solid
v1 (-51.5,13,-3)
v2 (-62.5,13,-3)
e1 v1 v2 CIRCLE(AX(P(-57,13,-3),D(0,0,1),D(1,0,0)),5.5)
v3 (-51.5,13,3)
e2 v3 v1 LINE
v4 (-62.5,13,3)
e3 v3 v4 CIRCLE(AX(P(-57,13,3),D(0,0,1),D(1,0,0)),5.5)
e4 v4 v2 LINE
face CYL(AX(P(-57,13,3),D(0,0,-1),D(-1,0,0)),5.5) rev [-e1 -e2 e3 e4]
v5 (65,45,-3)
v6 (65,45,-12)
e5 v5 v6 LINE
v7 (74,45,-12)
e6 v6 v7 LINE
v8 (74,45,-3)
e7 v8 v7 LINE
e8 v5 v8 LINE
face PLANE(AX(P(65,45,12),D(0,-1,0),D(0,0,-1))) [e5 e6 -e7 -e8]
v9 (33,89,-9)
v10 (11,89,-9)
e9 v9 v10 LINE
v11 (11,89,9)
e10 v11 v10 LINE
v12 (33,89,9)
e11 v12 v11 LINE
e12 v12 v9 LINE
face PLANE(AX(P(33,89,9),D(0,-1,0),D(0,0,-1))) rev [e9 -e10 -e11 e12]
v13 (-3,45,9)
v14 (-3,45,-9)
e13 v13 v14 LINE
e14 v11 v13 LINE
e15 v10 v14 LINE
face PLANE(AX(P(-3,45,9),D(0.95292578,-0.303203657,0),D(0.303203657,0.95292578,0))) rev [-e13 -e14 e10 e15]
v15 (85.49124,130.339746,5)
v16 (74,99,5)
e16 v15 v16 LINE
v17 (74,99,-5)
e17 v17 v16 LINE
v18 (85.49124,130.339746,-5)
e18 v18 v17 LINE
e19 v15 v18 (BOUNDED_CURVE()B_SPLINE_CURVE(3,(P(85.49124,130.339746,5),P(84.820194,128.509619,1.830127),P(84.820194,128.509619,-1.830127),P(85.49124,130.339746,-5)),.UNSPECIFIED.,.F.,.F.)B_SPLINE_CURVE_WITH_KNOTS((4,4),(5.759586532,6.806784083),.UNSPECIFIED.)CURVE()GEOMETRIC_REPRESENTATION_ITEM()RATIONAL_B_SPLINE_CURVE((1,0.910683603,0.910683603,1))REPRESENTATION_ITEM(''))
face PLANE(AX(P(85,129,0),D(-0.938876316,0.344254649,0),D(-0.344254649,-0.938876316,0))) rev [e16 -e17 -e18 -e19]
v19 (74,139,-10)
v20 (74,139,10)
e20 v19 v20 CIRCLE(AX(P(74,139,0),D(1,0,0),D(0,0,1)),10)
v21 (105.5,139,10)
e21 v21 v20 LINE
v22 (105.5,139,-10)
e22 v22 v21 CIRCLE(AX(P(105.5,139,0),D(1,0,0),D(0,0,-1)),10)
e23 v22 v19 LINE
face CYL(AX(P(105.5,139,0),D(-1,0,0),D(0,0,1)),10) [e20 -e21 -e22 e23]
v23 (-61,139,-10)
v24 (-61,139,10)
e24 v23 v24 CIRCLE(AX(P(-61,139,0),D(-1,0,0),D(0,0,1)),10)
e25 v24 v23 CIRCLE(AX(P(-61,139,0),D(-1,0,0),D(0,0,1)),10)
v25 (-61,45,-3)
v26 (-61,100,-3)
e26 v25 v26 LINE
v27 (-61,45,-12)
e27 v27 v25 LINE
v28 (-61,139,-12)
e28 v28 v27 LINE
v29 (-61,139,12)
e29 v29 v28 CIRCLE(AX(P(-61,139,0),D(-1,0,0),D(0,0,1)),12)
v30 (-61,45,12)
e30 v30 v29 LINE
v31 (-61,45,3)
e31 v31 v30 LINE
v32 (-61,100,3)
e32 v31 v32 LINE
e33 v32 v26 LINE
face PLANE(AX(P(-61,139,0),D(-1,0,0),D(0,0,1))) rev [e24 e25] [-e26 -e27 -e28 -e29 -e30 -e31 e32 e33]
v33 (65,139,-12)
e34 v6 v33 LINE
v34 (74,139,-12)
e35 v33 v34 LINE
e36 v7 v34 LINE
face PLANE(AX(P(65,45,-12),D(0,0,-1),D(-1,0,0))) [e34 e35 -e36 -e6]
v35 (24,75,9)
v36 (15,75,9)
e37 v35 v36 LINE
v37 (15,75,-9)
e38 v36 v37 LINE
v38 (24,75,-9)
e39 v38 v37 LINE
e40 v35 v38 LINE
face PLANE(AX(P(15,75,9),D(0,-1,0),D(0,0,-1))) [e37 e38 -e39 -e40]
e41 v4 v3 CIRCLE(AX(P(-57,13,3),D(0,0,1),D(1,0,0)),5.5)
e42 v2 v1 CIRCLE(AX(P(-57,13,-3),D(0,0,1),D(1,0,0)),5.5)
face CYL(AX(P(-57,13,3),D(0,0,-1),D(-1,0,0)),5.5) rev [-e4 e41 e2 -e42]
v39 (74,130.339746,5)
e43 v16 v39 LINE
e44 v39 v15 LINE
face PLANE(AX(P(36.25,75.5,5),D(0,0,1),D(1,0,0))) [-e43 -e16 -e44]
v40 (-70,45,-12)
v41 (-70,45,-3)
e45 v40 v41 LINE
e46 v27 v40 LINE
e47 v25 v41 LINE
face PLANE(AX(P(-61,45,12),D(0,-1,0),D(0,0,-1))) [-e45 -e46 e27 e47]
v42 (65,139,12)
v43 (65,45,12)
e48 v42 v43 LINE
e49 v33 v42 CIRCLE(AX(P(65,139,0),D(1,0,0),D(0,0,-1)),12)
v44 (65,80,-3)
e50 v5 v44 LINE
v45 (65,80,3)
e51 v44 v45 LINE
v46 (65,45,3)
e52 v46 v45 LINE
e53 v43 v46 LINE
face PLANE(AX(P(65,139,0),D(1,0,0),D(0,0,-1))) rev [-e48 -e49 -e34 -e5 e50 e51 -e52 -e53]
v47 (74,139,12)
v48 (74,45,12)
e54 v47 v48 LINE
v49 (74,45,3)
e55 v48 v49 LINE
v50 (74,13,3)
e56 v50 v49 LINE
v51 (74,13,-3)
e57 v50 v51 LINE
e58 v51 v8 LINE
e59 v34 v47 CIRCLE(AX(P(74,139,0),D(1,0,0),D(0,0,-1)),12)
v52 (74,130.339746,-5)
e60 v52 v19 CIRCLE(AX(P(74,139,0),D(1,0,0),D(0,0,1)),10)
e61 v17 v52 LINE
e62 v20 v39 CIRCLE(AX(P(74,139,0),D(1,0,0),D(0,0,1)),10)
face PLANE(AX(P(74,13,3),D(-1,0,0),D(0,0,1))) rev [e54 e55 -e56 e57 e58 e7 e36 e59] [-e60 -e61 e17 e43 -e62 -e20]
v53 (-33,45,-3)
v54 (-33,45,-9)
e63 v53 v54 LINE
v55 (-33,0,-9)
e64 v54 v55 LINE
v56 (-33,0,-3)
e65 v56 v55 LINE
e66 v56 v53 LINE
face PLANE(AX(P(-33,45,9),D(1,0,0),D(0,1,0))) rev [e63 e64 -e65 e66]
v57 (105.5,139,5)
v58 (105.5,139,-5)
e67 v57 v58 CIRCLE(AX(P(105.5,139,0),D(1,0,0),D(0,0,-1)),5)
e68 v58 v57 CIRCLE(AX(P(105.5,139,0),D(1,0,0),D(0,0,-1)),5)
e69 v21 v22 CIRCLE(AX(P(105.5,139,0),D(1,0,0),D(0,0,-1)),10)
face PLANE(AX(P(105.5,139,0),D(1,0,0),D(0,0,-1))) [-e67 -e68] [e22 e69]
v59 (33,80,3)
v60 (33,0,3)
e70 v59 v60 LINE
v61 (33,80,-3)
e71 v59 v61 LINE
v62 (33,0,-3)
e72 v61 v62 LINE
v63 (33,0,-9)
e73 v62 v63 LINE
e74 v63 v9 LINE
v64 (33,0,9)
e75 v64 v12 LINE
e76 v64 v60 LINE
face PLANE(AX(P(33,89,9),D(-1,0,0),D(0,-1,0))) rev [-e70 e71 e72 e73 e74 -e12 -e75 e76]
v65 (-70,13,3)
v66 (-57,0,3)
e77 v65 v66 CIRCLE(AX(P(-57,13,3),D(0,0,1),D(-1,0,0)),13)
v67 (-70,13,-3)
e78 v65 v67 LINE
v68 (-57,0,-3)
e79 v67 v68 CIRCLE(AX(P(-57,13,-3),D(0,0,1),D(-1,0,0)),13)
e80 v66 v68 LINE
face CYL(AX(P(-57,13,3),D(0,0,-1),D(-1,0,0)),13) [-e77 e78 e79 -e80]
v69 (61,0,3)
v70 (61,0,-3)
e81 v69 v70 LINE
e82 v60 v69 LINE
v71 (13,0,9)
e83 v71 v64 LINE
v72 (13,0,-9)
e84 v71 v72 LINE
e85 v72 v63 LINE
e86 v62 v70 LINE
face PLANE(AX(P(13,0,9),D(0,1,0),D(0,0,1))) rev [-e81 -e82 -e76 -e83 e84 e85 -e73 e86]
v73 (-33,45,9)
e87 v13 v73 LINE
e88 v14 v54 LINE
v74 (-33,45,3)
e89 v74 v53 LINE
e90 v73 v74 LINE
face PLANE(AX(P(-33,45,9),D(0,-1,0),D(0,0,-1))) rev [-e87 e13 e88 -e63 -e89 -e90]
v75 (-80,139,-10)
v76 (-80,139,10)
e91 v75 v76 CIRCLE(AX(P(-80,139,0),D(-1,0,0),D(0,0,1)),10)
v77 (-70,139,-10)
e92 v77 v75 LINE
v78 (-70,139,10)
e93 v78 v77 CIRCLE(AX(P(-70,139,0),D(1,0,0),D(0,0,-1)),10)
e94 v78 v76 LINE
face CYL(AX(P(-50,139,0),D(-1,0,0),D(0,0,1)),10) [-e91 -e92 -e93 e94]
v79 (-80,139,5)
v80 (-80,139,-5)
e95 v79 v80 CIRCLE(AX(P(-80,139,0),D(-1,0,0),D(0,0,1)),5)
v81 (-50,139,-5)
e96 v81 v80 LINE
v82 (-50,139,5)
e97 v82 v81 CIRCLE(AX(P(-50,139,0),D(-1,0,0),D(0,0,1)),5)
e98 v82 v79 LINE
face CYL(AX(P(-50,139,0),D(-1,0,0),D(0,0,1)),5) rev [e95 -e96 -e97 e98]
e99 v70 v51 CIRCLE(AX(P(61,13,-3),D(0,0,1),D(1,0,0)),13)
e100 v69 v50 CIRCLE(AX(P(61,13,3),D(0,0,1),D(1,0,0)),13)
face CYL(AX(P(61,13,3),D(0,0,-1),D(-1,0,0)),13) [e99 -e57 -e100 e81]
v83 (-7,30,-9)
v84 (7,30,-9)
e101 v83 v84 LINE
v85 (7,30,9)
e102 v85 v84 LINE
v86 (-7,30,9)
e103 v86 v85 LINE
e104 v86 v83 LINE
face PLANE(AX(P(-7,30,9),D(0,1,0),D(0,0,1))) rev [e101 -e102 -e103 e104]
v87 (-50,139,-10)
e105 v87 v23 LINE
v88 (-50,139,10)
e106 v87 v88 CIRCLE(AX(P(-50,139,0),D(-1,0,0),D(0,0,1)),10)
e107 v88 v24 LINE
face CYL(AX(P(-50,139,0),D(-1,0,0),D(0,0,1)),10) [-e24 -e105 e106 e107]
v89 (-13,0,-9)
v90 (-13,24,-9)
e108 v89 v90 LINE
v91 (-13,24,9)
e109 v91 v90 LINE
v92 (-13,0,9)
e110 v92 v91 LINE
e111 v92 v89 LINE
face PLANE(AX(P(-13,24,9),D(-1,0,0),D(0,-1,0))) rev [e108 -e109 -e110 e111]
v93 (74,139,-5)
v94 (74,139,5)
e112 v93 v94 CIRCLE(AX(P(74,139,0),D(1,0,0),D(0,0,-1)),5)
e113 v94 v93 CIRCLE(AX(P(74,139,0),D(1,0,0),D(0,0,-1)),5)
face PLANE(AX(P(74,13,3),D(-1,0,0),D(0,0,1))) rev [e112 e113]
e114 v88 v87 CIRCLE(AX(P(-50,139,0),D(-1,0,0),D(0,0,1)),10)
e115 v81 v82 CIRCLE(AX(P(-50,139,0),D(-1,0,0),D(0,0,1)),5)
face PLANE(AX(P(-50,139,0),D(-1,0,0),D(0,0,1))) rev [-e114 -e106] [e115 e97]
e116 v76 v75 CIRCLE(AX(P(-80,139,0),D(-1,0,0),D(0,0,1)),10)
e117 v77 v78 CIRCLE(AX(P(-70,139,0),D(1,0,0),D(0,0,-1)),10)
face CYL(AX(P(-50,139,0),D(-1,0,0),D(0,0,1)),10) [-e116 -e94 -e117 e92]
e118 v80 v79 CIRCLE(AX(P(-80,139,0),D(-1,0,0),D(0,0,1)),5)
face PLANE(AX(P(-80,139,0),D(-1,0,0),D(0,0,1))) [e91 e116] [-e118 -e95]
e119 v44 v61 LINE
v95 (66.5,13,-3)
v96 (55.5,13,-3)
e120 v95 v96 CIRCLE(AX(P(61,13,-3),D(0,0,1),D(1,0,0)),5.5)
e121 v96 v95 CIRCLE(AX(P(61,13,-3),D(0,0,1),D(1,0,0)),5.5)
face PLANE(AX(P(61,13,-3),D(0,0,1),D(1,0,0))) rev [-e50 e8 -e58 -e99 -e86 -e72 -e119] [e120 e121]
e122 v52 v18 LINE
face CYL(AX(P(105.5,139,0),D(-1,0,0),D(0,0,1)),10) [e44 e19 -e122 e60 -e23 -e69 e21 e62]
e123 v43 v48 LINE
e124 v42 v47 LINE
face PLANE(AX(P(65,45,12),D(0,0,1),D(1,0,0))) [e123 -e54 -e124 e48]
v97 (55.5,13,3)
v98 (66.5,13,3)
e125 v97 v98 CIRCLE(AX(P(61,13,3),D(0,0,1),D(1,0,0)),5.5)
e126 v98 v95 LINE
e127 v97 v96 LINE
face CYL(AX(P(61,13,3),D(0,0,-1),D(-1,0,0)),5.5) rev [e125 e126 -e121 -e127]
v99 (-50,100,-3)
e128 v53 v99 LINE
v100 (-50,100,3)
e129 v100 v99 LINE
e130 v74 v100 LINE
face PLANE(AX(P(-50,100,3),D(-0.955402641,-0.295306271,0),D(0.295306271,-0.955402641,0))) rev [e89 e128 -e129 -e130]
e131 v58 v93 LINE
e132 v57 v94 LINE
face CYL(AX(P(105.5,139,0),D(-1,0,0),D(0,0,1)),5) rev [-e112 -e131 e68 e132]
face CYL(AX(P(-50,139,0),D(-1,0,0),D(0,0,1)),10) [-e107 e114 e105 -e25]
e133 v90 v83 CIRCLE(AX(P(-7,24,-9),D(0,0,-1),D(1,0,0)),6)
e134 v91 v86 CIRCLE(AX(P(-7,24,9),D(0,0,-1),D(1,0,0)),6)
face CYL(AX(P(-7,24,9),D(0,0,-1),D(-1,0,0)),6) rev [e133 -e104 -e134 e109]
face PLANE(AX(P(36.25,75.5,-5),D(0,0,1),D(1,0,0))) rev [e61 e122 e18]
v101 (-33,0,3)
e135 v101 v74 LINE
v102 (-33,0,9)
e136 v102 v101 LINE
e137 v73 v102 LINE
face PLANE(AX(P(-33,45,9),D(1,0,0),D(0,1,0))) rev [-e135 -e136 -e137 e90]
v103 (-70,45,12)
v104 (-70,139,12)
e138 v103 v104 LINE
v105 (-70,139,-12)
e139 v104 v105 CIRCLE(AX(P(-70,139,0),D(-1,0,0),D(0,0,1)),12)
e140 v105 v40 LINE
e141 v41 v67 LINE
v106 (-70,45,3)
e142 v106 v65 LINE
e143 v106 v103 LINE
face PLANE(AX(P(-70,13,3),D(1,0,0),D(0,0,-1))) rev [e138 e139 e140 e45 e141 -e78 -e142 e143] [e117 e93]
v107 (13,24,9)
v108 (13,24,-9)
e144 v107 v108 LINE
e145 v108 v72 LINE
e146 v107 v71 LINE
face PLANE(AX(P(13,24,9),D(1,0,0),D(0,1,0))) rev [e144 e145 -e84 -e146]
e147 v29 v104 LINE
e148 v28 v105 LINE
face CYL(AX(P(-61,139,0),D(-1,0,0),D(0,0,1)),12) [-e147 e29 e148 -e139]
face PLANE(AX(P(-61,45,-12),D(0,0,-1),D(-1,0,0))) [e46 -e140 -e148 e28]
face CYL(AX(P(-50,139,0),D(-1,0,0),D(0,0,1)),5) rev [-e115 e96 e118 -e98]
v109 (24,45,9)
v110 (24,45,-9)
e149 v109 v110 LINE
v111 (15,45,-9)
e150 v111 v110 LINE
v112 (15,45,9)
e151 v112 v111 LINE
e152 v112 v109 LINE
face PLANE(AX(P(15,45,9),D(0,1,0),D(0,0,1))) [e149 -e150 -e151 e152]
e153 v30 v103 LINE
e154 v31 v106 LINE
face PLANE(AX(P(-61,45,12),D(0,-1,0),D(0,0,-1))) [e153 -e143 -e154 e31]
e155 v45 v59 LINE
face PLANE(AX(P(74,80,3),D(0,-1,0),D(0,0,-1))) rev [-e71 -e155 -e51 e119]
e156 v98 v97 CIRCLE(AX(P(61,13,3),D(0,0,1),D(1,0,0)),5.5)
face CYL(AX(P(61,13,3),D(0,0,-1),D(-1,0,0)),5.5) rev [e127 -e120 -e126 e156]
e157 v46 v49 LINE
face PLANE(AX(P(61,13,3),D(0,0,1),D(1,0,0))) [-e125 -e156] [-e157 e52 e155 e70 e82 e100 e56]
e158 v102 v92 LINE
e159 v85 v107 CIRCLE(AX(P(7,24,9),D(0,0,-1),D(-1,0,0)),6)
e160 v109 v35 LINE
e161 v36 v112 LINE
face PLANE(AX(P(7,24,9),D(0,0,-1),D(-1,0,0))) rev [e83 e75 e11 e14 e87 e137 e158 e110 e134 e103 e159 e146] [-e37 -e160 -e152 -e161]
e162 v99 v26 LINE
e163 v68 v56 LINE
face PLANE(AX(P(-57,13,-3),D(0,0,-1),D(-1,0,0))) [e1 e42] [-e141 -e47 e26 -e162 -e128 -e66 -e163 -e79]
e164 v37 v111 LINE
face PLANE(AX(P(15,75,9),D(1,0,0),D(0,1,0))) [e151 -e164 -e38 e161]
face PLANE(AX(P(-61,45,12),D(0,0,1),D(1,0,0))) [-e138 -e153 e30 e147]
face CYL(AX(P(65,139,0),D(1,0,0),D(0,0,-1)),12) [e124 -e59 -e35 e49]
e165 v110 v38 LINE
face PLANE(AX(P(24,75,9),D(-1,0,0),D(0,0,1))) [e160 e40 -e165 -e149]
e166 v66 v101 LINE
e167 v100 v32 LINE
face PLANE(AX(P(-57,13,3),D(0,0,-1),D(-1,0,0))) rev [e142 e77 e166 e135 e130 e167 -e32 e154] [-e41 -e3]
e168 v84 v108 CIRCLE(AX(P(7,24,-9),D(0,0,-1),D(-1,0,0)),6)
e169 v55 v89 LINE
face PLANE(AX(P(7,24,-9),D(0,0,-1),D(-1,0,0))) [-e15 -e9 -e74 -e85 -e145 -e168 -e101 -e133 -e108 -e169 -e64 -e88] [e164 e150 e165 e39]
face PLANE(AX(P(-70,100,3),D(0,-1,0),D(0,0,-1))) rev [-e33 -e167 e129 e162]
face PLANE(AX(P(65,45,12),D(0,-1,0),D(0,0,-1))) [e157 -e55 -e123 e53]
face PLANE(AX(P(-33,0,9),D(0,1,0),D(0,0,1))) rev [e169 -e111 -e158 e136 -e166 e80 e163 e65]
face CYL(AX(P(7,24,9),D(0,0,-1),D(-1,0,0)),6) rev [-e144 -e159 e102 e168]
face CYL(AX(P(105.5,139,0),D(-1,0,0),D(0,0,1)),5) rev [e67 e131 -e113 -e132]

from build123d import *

# Parameters (mm, degrees)
BASE_PLATE_SKETCH_W            = 9
BASE_PLATE_SKETCH_H            = 30
BASE_PLATE_DEPTH               = 9
LEFT_ARM_SKETCH_R              = 5.5
LEFT_ARM_DEPTH                 = 3
LEFT_ARM_UPRIGHT_DEPTH         = 9
LEFT_PIVOT_BOSS_SKETCH_R       = 10
LEFT_PIVOT_BOSS_SKETCH_R_2     = 5
LEFT_PIVOT_BOSS_20_DEPTH       = 31.5
LEFT_GUSSET_RIB_REACH          = 186.595
LEFT_GUSSET_SKETCH_WALL_W      = 403.142743776
LEFT_GUSSET_SKETCH_WALL_H      = 10
RIGHT_ARM_SKETCH_R             = 5.5
RIGHT_ARM_DEPTH                = 3
RIGHT_START                    = -9
RIGHT_ARM_UPRIGHT_DEPTH        = 9
RIGHT_PIVOT_BOSS_20_DEPTH      = 10
RIGHT_PIVOT_BOSS_20_DEPTH_BACK = 20
RIGHT_PIVOT_BOSS_SKETCH_R      = 10
RIGHT_PIVOT_BOSS_SKETCH_R_2    = 5
PIVOT_START                    = -38
PIVOT_CUT_SKETCH_R             = 5
PIVOT_CUT_DEPTH                = 38


with BuildPart() as part:
    # Base Plate Sketch → Base Plate (new, symmetric)
    with BuildSketch(Plane.XY):
        with BuildLine():
            Line((-7, 30), (7, 30))
            ThreePointArc((7, 30), (11.242640687, 28.242640687), (13, 24))
            Line((13, 24), (13, 0))
            Line((13, 0), (33, 0))
            Line((33, 0), (33, 89))
            Line((33, 89), (11, 89))
            Line((11, 89), (-3, 45))
            Line((-3, 45), (-33, 45))
            Line((-33, 45), (-33, 0))
            Line((-33, 0), (-13, 0))
            Line((-13, 0), (-13, 24))
            ThreePointArc((-13, 24), (-11.242640687, 28.242640687), (-7, 30))
        make_face()
        with Locations((19.5, 60)):
            Rectangle(BASE_PLATE_SKETCH_W, BASE_PLATE_SKETCH_H, mode=Mode.SUBTRACT)
    extrude(amount=BASE_PLATE_DEPTH, both=True)

    # Left Arm Sketch → Left Arm (add, symmetric)
    with BuildSketch(Plane.XY):
        with BuildLine():
            Line((33, 0), (61, 0))
            ThreePointArc((61, 0), (70.192388155, 3.807611845), (74, 13))
            Line((74, 13), (74, 80))
            Line((74, 80), (33, 80))
            Line((33, 80), (33, 0))
        make_face()
        with Locations((61, 13)):
            Circle(LEFT_ARM_SKETCH_R, mode=Mode.SUBTRACT)
    extrude(amount=LEFT_ARM_DEPTH, both=True)

    # Left Arm Upright Sketch → Left Arm Upright (add)
    with BuildSketch(Plane(origin=(74, 0, 0), x_dir=(0, 0, -1), z_dir=(1, 0, 0))):
        with BuildLine():
            Line((-12, 45), (12, 45))
            Line((12, 45), (12, 139))
            ThreePointArc((12, 139), (0, 151), (-12, 139))
            Line((-12, 139), (-12, 45))
        make_face()
    extrude(amount=-LEFT_ARM_UPRIGHT_DEPTH)

    # Left Pivot Boss Sketch → Left Pivot Boss Ø20 (add)
    with BuildSketch(Plane(origin=(74, 0, 0), x_dir=(0, 0, -1), z_dir=(1, 0, 0))):
        with Locations(Location((0, 139, 0), (0, 0, 180))):
            Circle(LEFT_PIVOT_BOSS_SKETCH_R)
        with Locations((0, 139)):
            Circle(LEFT_PIVOT_BOSS_SKETCH_R_2, mode=Mode.SUBTRACT)
    extrude(amount=LEFT_PIVOT_BOSS_20_DEPTH)

    # Left Gusset Sketch wall → Left Gusset Rib (add, up to next)
    with BuildSketch(Plane(origin=(79.5, 114, 0), x_dir=(-0.344254649158, -0.938876315887, 0), z_dir=(0.938876315887, -0.344254649158, 0)), mode=Mode.PRIVATE) as left_gusset_rib_sk1:
        Rectangle(LEFT_GUSSET_SKETCH_WALL_W, LEFT_GUSSET_SKETCH_WALL_H)
    left_gusset_rib_tool1 = extrude(left_gusset_rib_sk1.sketch, amount=-LEFT_GUSSET_RIB_REACH, mode=Mode.PRIVATE) - part.part
    add(left_gusset_rib_tool1.solids().sort_by_distance((79.5, 114, 0))[0])

    # Right Arm Sketch → Right Arm (add, symmetric)
    with BuildSketch(Plane.XY):
        with BuildLine():
            Line((-33, 0), (-57, 0))
            ThreePointArc((-57, 0), (-66.192388155, 3.807611845), (-70, 13))
            Line((-70, 13), (-70, 100))
            Line((-70, 100), (-50, 100))
            Line((-50, 100), (-33, 45))
            Line((-33, 45), (-33, 0))
        make_face()
        with Locations((-57, 13)):
            Circle(RIGHT_ARM_SKETCH_R, mode=Mode.SUBTRACT)
    extrude(amount=RIGHT_ARM_DEPTH, both=True)

    # Right Arm Upright Sketch → Right Arm Upright (add)
    with BuildSketch(Plane.ZY.offset(70).offset(RIGHT_START)):
        with BuildLine():
            Line((12, 45), (-12, 45))
            Line((-12, 45), (-12, 139))
            ThreePointArc((-12, 139), (0, 151), (12, 139))
            Line((12, 139), (12, 45))
        make_face()
    extrude(amount=RIGHT_ARM_UPRIGHT_DEPTH)

    # Right Pivot Boss Sketch → Right Pivot Boss Ø20 (add, two sides: drawn at the far end of the back side and taken through both)
    with BuildSketch(Plane.ZY.offset(70).offset(-RIGHT_PIVOT_BOSS_20_DEPTH_BACK)):
        with Locations(Location((0, 139, 0), (0, 0, 300))):
            Circle(RIGHT_PIVOT_BOSS_SKETCH_R)
        with Locations(Location((0, 139, 0), (0, 0, 180))):
            Circle(RIGHT_PIVOT_BOSS_SKETCH_R_2, mode=Mode.SUBTRACT)
    extrude(amount=RIGHT_PIVOT_BOSS_20_DEPTH + RIGHT_PIVOT_BOSS_20_DEPTH_BACK)

    # Pivot Cut Sketch → Pivot Cut (cut)
    with BuildSketch(Plane(origin=(-50, 0, 0), x_dir=(0, 0, -1), z_dir=(1, 0, 0)).offset(PIVOT_START)):
        with Locations((0, 139)):
            Circle(PIVOT_CUT_SKETCH_R)
    extrude(amount=PIVOT_CUT_DEPTH, mode=Mode.SUBTRACT)


solid = part.part
